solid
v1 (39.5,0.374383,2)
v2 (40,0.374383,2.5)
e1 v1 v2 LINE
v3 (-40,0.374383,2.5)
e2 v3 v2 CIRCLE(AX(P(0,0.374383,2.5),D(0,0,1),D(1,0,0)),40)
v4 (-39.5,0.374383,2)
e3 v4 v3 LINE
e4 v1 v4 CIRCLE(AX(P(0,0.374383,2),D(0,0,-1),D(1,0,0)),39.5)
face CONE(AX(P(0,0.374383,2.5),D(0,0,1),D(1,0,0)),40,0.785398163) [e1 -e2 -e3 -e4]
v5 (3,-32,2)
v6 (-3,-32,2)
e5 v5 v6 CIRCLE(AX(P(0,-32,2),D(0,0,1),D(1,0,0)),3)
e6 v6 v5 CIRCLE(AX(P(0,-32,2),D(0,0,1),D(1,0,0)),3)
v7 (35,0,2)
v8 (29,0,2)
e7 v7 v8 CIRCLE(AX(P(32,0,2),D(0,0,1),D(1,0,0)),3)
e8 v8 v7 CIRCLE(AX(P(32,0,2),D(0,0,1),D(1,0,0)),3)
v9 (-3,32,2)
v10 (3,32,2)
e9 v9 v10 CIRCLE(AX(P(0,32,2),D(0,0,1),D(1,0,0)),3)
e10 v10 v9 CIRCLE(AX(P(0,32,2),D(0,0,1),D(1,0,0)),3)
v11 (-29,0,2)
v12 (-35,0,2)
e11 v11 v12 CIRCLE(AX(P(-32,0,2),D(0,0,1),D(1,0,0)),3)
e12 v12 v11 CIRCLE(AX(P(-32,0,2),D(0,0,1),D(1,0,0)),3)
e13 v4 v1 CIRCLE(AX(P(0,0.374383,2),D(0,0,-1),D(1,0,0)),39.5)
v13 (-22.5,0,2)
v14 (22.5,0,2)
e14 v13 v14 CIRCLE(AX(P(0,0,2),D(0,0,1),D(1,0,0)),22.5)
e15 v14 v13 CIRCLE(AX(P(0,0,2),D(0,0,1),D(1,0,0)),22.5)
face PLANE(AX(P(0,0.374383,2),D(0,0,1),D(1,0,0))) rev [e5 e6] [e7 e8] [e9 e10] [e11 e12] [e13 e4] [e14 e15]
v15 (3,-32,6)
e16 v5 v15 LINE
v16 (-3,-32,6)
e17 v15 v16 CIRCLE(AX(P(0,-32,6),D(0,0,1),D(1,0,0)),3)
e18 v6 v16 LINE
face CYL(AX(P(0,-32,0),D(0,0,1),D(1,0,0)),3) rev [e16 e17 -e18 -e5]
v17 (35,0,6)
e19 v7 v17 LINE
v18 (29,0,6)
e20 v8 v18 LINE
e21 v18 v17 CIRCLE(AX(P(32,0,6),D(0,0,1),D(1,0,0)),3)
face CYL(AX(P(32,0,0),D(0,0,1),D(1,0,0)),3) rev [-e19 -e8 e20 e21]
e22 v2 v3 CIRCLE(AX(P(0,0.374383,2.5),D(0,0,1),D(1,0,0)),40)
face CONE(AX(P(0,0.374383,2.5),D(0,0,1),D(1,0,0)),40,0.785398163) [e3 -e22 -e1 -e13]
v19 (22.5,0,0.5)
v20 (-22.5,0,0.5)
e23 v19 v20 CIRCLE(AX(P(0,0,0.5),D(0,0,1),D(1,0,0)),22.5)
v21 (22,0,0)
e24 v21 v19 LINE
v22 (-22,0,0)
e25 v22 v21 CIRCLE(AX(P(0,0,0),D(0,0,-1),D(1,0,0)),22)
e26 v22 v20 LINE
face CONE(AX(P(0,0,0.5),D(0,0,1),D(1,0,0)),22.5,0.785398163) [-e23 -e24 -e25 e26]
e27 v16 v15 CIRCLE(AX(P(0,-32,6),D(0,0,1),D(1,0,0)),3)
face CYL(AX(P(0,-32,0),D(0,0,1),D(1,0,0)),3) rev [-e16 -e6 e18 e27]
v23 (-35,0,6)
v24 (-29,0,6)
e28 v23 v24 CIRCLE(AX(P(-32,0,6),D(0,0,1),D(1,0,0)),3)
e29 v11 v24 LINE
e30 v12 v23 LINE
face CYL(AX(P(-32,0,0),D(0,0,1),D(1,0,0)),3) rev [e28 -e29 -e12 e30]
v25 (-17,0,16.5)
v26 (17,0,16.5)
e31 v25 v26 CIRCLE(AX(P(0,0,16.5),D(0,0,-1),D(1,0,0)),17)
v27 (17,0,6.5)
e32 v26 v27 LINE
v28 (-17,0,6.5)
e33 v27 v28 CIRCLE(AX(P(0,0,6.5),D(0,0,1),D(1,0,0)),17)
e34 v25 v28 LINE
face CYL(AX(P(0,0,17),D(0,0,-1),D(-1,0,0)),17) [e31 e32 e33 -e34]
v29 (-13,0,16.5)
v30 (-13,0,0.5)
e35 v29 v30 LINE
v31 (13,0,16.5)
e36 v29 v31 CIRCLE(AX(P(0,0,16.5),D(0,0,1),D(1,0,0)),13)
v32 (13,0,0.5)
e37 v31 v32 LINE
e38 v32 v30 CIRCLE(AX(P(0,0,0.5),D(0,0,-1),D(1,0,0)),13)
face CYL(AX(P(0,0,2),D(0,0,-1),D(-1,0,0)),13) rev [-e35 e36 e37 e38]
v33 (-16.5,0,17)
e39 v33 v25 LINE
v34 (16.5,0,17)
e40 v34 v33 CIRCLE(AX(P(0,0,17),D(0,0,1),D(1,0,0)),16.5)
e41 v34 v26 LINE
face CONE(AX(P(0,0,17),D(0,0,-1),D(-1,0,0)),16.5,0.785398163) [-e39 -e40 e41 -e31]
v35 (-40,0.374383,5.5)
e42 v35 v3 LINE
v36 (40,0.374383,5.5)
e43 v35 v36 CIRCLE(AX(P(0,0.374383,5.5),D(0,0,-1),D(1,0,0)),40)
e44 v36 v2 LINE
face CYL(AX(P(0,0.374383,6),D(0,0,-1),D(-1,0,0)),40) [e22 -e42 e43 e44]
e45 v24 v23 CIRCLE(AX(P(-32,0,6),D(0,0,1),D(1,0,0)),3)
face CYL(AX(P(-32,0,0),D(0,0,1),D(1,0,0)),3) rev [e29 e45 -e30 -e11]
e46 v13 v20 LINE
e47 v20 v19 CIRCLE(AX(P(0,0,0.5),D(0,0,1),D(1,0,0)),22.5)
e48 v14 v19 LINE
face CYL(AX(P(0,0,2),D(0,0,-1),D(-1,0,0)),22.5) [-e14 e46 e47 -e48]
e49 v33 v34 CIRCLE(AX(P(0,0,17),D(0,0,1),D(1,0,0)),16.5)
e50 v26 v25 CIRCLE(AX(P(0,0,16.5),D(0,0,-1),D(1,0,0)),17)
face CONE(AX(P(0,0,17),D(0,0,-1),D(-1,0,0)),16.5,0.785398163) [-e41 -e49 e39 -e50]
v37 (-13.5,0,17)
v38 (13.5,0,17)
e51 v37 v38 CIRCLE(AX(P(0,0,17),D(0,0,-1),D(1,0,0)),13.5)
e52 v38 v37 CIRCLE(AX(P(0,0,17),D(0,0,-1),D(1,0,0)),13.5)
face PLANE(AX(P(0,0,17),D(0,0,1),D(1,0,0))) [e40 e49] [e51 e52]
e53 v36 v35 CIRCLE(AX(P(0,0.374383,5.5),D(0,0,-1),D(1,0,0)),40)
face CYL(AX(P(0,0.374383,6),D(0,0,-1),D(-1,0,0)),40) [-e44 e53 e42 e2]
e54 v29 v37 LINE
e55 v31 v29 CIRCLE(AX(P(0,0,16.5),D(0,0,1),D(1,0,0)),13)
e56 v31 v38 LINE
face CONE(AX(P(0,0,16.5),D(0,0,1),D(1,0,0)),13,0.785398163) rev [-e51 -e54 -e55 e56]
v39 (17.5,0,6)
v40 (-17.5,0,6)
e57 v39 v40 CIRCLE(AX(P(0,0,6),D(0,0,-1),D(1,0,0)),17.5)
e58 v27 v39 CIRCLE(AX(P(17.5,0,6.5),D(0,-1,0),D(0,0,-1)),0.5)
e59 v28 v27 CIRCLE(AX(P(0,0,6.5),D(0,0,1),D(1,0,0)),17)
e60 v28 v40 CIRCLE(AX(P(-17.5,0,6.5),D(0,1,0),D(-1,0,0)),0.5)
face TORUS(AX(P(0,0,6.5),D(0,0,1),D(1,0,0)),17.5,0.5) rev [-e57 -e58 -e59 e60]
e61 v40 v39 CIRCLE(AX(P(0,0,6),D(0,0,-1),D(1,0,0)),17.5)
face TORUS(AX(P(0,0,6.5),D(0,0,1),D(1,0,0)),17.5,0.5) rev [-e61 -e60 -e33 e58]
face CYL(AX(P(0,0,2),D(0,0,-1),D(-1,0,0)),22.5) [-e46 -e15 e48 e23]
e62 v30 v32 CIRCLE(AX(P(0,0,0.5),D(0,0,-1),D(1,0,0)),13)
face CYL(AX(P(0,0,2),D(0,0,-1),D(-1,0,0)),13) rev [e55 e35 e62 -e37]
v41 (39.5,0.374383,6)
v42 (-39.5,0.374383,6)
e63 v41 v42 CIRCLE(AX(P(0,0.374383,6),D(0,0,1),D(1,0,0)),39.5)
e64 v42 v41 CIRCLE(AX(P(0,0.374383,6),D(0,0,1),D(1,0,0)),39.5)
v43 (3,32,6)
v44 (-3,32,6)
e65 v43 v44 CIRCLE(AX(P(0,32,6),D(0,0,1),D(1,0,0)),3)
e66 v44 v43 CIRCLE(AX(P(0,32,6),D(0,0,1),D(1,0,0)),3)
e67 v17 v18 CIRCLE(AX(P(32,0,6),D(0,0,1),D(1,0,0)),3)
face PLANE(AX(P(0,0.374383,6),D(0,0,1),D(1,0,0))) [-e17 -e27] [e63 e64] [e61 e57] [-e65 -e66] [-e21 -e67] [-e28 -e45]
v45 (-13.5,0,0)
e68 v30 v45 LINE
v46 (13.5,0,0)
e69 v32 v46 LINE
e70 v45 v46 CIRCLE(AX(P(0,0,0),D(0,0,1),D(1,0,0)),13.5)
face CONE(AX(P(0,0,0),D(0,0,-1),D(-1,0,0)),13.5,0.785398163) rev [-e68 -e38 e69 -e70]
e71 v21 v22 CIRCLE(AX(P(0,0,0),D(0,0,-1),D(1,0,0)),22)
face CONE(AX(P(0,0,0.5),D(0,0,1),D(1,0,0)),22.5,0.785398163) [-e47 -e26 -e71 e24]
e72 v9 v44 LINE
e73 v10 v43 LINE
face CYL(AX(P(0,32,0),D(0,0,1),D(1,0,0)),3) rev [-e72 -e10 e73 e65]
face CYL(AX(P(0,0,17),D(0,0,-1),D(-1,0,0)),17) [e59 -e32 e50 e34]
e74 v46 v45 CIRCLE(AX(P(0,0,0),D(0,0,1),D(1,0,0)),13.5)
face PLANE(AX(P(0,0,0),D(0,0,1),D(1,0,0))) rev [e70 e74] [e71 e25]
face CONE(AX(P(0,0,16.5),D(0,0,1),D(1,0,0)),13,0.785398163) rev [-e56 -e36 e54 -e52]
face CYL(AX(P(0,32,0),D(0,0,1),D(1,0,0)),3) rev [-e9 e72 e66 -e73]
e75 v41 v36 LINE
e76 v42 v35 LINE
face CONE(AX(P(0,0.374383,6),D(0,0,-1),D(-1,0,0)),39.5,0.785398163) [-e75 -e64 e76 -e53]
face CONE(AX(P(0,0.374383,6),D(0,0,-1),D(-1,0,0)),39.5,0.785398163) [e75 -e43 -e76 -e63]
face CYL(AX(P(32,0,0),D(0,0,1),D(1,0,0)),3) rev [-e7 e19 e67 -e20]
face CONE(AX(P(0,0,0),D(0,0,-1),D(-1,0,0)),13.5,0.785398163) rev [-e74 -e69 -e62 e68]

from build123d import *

# Parameters (mm, degrees)
SKETCH_1_R          = 22.5
SKETCH_1_R_2        = 13
EXTRUDE_1_DEPTH     = 2
SKETCH_2_R          = 40
SKETCH_2_R_2        = 13
EXTRUDE_2_DEPTH     = 4
SKETCH_3_R          = 17
SKETCH_3_R_2        = 13
EXTRUDE_3_DEPTH     = 11
CHAMFER_1_SIZE      = 0.5
FILLET_1_R          = 0.5
SKETCH_4_R          = 3
CUT_EXTRUDE_1_DEPTH = 58.888606929


with BuildPart() as part:
    # 草图1 → 拉伸1 (new body)
    with BuildSketch(Plane.XY):
        Circle(SKETCH_1_R)
        Circle(SKETCH_1_R_2, mode=Mode.SUBTRACT)
    extrude(amount=EXTRUDE_1_DEPTH)

    # 草图2 → 拉伸2 (add)
    with BuildSketch(Plane.XY.offset(2)):
        with Locations((0, 0.374383119)):
            Circle(SKETCH_2_R)
        Circle(SKETCH_2_R_2, mode=Mode.SUBTRACT)
    extrude(amount=EXTRUDE_2_DEPTH)

    # 草图3 → 拉伸3 (add)
    with BuildSketch(Plane.XY.offset(6)):
        Circle(SKETCH_3_R)
        Circle(SKETCH_3_R_2, mode=Mode.SUBTRACT)
    extrude(amount=EXTRUDE_3_DEPTH)

    # 倒角1
    chamfer_1_edges = [part.edges().sort_by_distance(p)[0] for p in [
        (-40, 0.374383119, 2),
        (-17, 0, 17),
        (-13, 0, 17),
        (-22.5, 0, 0),
        (-13, 0, 0),
        (-40, 0.374383119, 6),
    ]]
    chamfer(chamfer_1_edges, length=CHAMFER_1_SIZE)

    # 圆角1
    fillet_1_edges = [part.edges().sort_by_distance(p)[0] for p in [
        (-17, 0, 6),
    ]]
    fillet(fillet_1_edges, radius=FILLET_1_R)

    # 草图4 → 切除-拉伸1 (cut, through all)
    with BuildSketch(Plane.XY.offset(6)):
        with Locations((0, 32)):
            Circle(SKETCH_4_R)
        with Locations((-32, 0)):
            Circle(SKETCH_4_R)
        with Locations((0, -32)):
            Circle(SKETCH_4_R)
        with Locations((32, 0)):
            Circle(SKETCH_4_R)
    extrude(amount=-CUT_EXTRUDE_1_DEPTH, mode=Mode.SUBTRACT)


solid = part.part
